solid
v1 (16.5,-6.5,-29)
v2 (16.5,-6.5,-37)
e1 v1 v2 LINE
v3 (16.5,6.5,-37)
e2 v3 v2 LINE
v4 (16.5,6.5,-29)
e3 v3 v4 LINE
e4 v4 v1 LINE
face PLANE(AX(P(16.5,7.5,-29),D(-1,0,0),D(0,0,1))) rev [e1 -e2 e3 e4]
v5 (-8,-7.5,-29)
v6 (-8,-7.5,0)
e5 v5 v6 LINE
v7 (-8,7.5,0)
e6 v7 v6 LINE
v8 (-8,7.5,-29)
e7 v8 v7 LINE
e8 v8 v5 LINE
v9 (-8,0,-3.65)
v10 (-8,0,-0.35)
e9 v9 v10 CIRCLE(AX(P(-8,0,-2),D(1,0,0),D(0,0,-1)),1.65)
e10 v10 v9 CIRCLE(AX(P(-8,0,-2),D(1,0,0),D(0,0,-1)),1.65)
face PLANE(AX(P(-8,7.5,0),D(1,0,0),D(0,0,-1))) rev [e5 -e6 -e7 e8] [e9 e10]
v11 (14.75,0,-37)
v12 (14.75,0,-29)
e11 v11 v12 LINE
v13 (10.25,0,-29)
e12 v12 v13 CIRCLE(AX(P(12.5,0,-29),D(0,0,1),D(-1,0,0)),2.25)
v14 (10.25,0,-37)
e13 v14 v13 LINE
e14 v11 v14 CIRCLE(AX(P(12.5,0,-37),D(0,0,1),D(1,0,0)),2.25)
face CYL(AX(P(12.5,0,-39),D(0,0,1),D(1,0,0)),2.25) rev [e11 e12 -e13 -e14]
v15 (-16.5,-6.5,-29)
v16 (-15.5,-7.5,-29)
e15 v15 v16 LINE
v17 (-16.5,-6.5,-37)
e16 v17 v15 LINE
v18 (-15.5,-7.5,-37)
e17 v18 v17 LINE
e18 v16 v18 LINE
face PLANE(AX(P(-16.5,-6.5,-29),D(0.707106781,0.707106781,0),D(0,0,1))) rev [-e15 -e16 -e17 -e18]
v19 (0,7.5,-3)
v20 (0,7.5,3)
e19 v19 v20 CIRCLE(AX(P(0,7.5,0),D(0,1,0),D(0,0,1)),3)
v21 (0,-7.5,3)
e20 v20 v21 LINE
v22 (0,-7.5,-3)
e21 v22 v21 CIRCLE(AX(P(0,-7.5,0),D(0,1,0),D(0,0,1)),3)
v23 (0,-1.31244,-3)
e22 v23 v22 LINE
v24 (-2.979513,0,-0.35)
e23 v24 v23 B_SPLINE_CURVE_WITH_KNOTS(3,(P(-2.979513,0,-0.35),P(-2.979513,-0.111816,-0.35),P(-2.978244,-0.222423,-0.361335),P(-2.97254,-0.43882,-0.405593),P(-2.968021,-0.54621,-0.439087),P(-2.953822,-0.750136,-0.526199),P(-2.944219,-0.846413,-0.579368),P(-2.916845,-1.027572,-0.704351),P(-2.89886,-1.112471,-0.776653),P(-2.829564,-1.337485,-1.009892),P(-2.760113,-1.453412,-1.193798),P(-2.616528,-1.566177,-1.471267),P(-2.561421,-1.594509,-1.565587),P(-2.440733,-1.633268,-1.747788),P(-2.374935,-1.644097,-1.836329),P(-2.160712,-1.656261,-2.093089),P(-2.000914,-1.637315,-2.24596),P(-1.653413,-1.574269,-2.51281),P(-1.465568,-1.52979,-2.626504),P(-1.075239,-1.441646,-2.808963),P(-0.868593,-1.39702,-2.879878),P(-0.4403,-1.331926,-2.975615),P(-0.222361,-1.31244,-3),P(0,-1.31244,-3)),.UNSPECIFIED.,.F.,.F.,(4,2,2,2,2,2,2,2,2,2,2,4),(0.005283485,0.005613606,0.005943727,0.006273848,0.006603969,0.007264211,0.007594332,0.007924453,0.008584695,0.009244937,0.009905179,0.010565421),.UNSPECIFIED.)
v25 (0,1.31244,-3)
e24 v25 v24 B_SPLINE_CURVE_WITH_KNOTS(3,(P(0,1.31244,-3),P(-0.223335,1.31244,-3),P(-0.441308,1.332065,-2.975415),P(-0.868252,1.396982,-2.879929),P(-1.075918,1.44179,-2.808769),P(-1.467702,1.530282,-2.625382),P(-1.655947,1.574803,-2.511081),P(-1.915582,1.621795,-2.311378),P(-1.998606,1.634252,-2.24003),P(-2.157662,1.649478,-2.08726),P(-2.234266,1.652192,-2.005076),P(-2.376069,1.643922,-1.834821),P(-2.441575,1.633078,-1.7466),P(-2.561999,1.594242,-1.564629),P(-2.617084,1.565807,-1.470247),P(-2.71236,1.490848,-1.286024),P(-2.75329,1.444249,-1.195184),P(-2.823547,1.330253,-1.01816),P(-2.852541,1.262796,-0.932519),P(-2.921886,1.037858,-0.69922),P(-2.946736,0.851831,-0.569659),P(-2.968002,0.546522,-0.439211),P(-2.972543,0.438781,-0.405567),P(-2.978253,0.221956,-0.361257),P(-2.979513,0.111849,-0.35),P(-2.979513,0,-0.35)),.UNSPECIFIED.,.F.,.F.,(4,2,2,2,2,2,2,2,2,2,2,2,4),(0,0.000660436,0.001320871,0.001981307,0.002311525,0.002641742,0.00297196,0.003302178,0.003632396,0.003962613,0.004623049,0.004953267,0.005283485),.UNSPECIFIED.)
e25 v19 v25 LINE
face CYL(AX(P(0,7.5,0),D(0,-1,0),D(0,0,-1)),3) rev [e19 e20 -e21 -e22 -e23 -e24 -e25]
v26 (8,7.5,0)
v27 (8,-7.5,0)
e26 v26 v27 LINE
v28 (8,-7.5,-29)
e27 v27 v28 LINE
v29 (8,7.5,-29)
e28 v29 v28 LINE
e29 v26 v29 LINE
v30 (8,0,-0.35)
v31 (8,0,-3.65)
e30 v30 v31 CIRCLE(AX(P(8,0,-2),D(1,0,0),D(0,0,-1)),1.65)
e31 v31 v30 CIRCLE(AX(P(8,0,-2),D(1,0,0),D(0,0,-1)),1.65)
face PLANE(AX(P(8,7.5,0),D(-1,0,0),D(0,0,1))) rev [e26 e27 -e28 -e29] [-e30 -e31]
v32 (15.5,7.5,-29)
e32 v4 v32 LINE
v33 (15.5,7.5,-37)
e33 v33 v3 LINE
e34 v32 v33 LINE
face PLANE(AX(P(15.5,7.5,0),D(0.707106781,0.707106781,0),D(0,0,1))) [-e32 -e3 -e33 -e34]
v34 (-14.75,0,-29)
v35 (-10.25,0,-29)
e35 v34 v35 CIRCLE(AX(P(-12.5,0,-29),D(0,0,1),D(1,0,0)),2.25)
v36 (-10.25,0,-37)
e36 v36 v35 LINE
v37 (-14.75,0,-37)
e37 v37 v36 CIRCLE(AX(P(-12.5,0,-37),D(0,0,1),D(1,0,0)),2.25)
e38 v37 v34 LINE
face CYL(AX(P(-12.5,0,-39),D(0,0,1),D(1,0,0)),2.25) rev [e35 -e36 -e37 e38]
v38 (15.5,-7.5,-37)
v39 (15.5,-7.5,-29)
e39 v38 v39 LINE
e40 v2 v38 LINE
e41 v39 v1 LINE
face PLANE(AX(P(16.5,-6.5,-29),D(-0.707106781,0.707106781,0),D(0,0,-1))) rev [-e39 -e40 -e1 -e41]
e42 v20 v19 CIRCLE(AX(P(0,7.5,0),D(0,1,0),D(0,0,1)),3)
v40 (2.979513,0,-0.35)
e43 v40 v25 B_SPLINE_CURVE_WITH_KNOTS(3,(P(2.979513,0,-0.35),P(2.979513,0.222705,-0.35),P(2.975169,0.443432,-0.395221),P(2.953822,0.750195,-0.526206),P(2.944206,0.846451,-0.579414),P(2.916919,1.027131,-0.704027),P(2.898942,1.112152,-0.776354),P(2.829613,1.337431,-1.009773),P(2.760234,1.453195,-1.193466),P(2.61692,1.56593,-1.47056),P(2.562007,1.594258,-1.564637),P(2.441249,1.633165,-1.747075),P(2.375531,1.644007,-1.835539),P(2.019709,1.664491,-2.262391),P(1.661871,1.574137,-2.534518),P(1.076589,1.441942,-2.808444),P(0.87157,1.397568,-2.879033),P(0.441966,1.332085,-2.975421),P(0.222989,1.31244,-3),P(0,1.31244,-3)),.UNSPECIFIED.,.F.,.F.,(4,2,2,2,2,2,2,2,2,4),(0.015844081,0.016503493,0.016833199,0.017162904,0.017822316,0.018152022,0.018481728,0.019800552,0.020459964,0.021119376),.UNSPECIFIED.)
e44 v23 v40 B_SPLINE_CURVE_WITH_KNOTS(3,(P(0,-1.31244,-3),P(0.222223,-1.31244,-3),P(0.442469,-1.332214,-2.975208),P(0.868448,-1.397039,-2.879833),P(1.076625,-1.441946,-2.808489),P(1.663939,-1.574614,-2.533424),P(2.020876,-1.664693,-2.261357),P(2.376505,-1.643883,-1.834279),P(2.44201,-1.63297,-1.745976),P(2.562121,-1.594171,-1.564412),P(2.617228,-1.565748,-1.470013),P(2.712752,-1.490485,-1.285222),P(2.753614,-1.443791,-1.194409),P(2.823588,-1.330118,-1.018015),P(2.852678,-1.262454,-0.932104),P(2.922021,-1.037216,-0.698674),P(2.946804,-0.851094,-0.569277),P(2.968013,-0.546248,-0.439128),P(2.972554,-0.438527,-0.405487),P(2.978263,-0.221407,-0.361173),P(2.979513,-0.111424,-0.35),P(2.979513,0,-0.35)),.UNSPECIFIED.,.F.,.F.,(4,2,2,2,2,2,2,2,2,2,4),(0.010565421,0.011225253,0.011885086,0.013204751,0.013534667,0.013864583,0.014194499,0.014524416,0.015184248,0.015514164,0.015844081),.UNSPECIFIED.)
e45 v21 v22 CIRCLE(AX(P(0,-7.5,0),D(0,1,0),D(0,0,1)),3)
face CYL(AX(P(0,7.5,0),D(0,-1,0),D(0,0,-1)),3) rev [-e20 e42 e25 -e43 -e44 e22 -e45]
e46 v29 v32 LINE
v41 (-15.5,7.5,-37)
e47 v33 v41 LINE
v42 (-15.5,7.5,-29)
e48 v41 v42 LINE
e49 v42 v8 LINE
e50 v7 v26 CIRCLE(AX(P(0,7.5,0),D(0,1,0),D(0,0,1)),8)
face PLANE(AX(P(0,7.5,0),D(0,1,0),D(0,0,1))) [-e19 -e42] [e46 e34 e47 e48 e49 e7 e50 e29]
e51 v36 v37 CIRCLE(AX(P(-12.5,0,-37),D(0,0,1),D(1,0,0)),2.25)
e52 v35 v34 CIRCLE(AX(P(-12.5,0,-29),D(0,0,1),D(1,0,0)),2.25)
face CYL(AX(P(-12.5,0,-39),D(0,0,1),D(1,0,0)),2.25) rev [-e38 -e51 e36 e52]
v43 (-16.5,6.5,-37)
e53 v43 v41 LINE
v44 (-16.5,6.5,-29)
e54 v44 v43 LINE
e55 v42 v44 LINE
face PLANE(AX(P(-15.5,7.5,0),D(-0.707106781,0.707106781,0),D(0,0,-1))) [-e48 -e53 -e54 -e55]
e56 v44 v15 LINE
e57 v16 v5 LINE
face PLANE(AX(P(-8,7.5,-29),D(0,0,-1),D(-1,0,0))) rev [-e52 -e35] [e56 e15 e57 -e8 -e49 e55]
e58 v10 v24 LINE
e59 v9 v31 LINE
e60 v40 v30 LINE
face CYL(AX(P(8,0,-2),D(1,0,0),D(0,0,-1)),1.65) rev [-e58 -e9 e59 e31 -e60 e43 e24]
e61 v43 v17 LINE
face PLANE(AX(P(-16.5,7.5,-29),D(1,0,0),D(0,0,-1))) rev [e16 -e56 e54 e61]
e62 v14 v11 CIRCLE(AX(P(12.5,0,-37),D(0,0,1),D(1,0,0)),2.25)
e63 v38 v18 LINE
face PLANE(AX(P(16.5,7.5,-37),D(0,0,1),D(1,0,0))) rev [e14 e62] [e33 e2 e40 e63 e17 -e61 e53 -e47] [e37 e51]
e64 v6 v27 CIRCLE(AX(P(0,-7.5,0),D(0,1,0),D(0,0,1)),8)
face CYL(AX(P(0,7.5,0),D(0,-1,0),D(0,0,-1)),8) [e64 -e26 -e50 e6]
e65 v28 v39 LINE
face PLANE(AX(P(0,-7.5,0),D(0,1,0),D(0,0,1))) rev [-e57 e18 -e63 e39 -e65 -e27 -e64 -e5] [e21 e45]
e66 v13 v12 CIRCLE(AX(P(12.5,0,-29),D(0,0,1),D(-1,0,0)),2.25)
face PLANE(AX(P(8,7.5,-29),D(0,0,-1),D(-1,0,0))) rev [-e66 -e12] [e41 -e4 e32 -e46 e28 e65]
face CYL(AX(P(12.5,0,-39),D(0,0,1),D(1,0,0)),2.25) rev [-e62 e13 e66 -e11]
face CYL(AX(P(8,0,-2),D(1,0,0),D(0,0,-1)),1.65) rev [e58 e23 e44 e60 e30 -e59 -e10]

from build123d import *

# Parameters (mm, degrees)
SKETCH_1_R          = 3
EXTRUDE_1_DEPTH     = 7.5
HOLE_WIZARD_M4_1_D  = 3.3
SKETCH_5_R          = 2.25
CUT_EXTRUDE_1_DEPTH = 10
CHAMFER_1_SIZE      = 1


with BuildPart() as part:
    # 草图1 → 凸台-拉伸1 (new, symmetric)
    with BuildSketch(Plane(origin=(0, 0, 0), x_dir=(1, 0, 0), z_dir=(0, 1, 0))):
        with BuildLine():
            Line((-8, 0), (-8, 29))
            Line((-8, 29), (-16.5, 29))
            Line((-16.5, 29), (-16.5, 37))
            Line((-16.5, 37), (16.5, 37))
            Line((16.5, 37), (16.5, 29))
            Line((16.5, 29), (8, 29))
            Line((8, 29), (8, 0))
            ThreePointArc((8, 0), (0, -8), (-8, 0))
        make_face()
        with Locations(Location((0, 0, 0), (0, 0, 270))):
            Circle(SKETCH_1_R, mode=Mode.SUBTRACT)
    extrude(amount=EXTRUDE_1_DEPTH, both=True)

    # M4 螺纹孔1 (through all)
    with Locations(Plane(origin=(8, 0, 0), x_dir=(0, 0, -1), z_dir=(1, 0, 0))):
        with Locations((2, 0)):
            Hole(HOLE_WIZARD_M4_1_D / 2)

    # 草图5 → 切除-拉伸1 (cut)
    with BuildSketch(Plane.XY.offset(-29)):
        with Locations((-12.5, 0)):
            Circle(SKETCH_5_R)
        with Locations((12.5, 0)):
            Circle(SKETCH_5_R)
    extrude(amount=-CUT_EXTRUDE_1_DEPTH, mode=Mode.SUBTRACT)

    # 倒角1
    chamfer_1_edges = [part.edges().sort_by_distance(p)[0] for p in [
        (16.5, 7.5, -33),
        (-16.5, 7.5, -33),
        (-16.5, -7.5, -33),
        (16.5, -7.5, -33),
    ]]
    chamfer(chamfer_1_edges, length=CHAMFER_1_SIZE)


solid = part.part
